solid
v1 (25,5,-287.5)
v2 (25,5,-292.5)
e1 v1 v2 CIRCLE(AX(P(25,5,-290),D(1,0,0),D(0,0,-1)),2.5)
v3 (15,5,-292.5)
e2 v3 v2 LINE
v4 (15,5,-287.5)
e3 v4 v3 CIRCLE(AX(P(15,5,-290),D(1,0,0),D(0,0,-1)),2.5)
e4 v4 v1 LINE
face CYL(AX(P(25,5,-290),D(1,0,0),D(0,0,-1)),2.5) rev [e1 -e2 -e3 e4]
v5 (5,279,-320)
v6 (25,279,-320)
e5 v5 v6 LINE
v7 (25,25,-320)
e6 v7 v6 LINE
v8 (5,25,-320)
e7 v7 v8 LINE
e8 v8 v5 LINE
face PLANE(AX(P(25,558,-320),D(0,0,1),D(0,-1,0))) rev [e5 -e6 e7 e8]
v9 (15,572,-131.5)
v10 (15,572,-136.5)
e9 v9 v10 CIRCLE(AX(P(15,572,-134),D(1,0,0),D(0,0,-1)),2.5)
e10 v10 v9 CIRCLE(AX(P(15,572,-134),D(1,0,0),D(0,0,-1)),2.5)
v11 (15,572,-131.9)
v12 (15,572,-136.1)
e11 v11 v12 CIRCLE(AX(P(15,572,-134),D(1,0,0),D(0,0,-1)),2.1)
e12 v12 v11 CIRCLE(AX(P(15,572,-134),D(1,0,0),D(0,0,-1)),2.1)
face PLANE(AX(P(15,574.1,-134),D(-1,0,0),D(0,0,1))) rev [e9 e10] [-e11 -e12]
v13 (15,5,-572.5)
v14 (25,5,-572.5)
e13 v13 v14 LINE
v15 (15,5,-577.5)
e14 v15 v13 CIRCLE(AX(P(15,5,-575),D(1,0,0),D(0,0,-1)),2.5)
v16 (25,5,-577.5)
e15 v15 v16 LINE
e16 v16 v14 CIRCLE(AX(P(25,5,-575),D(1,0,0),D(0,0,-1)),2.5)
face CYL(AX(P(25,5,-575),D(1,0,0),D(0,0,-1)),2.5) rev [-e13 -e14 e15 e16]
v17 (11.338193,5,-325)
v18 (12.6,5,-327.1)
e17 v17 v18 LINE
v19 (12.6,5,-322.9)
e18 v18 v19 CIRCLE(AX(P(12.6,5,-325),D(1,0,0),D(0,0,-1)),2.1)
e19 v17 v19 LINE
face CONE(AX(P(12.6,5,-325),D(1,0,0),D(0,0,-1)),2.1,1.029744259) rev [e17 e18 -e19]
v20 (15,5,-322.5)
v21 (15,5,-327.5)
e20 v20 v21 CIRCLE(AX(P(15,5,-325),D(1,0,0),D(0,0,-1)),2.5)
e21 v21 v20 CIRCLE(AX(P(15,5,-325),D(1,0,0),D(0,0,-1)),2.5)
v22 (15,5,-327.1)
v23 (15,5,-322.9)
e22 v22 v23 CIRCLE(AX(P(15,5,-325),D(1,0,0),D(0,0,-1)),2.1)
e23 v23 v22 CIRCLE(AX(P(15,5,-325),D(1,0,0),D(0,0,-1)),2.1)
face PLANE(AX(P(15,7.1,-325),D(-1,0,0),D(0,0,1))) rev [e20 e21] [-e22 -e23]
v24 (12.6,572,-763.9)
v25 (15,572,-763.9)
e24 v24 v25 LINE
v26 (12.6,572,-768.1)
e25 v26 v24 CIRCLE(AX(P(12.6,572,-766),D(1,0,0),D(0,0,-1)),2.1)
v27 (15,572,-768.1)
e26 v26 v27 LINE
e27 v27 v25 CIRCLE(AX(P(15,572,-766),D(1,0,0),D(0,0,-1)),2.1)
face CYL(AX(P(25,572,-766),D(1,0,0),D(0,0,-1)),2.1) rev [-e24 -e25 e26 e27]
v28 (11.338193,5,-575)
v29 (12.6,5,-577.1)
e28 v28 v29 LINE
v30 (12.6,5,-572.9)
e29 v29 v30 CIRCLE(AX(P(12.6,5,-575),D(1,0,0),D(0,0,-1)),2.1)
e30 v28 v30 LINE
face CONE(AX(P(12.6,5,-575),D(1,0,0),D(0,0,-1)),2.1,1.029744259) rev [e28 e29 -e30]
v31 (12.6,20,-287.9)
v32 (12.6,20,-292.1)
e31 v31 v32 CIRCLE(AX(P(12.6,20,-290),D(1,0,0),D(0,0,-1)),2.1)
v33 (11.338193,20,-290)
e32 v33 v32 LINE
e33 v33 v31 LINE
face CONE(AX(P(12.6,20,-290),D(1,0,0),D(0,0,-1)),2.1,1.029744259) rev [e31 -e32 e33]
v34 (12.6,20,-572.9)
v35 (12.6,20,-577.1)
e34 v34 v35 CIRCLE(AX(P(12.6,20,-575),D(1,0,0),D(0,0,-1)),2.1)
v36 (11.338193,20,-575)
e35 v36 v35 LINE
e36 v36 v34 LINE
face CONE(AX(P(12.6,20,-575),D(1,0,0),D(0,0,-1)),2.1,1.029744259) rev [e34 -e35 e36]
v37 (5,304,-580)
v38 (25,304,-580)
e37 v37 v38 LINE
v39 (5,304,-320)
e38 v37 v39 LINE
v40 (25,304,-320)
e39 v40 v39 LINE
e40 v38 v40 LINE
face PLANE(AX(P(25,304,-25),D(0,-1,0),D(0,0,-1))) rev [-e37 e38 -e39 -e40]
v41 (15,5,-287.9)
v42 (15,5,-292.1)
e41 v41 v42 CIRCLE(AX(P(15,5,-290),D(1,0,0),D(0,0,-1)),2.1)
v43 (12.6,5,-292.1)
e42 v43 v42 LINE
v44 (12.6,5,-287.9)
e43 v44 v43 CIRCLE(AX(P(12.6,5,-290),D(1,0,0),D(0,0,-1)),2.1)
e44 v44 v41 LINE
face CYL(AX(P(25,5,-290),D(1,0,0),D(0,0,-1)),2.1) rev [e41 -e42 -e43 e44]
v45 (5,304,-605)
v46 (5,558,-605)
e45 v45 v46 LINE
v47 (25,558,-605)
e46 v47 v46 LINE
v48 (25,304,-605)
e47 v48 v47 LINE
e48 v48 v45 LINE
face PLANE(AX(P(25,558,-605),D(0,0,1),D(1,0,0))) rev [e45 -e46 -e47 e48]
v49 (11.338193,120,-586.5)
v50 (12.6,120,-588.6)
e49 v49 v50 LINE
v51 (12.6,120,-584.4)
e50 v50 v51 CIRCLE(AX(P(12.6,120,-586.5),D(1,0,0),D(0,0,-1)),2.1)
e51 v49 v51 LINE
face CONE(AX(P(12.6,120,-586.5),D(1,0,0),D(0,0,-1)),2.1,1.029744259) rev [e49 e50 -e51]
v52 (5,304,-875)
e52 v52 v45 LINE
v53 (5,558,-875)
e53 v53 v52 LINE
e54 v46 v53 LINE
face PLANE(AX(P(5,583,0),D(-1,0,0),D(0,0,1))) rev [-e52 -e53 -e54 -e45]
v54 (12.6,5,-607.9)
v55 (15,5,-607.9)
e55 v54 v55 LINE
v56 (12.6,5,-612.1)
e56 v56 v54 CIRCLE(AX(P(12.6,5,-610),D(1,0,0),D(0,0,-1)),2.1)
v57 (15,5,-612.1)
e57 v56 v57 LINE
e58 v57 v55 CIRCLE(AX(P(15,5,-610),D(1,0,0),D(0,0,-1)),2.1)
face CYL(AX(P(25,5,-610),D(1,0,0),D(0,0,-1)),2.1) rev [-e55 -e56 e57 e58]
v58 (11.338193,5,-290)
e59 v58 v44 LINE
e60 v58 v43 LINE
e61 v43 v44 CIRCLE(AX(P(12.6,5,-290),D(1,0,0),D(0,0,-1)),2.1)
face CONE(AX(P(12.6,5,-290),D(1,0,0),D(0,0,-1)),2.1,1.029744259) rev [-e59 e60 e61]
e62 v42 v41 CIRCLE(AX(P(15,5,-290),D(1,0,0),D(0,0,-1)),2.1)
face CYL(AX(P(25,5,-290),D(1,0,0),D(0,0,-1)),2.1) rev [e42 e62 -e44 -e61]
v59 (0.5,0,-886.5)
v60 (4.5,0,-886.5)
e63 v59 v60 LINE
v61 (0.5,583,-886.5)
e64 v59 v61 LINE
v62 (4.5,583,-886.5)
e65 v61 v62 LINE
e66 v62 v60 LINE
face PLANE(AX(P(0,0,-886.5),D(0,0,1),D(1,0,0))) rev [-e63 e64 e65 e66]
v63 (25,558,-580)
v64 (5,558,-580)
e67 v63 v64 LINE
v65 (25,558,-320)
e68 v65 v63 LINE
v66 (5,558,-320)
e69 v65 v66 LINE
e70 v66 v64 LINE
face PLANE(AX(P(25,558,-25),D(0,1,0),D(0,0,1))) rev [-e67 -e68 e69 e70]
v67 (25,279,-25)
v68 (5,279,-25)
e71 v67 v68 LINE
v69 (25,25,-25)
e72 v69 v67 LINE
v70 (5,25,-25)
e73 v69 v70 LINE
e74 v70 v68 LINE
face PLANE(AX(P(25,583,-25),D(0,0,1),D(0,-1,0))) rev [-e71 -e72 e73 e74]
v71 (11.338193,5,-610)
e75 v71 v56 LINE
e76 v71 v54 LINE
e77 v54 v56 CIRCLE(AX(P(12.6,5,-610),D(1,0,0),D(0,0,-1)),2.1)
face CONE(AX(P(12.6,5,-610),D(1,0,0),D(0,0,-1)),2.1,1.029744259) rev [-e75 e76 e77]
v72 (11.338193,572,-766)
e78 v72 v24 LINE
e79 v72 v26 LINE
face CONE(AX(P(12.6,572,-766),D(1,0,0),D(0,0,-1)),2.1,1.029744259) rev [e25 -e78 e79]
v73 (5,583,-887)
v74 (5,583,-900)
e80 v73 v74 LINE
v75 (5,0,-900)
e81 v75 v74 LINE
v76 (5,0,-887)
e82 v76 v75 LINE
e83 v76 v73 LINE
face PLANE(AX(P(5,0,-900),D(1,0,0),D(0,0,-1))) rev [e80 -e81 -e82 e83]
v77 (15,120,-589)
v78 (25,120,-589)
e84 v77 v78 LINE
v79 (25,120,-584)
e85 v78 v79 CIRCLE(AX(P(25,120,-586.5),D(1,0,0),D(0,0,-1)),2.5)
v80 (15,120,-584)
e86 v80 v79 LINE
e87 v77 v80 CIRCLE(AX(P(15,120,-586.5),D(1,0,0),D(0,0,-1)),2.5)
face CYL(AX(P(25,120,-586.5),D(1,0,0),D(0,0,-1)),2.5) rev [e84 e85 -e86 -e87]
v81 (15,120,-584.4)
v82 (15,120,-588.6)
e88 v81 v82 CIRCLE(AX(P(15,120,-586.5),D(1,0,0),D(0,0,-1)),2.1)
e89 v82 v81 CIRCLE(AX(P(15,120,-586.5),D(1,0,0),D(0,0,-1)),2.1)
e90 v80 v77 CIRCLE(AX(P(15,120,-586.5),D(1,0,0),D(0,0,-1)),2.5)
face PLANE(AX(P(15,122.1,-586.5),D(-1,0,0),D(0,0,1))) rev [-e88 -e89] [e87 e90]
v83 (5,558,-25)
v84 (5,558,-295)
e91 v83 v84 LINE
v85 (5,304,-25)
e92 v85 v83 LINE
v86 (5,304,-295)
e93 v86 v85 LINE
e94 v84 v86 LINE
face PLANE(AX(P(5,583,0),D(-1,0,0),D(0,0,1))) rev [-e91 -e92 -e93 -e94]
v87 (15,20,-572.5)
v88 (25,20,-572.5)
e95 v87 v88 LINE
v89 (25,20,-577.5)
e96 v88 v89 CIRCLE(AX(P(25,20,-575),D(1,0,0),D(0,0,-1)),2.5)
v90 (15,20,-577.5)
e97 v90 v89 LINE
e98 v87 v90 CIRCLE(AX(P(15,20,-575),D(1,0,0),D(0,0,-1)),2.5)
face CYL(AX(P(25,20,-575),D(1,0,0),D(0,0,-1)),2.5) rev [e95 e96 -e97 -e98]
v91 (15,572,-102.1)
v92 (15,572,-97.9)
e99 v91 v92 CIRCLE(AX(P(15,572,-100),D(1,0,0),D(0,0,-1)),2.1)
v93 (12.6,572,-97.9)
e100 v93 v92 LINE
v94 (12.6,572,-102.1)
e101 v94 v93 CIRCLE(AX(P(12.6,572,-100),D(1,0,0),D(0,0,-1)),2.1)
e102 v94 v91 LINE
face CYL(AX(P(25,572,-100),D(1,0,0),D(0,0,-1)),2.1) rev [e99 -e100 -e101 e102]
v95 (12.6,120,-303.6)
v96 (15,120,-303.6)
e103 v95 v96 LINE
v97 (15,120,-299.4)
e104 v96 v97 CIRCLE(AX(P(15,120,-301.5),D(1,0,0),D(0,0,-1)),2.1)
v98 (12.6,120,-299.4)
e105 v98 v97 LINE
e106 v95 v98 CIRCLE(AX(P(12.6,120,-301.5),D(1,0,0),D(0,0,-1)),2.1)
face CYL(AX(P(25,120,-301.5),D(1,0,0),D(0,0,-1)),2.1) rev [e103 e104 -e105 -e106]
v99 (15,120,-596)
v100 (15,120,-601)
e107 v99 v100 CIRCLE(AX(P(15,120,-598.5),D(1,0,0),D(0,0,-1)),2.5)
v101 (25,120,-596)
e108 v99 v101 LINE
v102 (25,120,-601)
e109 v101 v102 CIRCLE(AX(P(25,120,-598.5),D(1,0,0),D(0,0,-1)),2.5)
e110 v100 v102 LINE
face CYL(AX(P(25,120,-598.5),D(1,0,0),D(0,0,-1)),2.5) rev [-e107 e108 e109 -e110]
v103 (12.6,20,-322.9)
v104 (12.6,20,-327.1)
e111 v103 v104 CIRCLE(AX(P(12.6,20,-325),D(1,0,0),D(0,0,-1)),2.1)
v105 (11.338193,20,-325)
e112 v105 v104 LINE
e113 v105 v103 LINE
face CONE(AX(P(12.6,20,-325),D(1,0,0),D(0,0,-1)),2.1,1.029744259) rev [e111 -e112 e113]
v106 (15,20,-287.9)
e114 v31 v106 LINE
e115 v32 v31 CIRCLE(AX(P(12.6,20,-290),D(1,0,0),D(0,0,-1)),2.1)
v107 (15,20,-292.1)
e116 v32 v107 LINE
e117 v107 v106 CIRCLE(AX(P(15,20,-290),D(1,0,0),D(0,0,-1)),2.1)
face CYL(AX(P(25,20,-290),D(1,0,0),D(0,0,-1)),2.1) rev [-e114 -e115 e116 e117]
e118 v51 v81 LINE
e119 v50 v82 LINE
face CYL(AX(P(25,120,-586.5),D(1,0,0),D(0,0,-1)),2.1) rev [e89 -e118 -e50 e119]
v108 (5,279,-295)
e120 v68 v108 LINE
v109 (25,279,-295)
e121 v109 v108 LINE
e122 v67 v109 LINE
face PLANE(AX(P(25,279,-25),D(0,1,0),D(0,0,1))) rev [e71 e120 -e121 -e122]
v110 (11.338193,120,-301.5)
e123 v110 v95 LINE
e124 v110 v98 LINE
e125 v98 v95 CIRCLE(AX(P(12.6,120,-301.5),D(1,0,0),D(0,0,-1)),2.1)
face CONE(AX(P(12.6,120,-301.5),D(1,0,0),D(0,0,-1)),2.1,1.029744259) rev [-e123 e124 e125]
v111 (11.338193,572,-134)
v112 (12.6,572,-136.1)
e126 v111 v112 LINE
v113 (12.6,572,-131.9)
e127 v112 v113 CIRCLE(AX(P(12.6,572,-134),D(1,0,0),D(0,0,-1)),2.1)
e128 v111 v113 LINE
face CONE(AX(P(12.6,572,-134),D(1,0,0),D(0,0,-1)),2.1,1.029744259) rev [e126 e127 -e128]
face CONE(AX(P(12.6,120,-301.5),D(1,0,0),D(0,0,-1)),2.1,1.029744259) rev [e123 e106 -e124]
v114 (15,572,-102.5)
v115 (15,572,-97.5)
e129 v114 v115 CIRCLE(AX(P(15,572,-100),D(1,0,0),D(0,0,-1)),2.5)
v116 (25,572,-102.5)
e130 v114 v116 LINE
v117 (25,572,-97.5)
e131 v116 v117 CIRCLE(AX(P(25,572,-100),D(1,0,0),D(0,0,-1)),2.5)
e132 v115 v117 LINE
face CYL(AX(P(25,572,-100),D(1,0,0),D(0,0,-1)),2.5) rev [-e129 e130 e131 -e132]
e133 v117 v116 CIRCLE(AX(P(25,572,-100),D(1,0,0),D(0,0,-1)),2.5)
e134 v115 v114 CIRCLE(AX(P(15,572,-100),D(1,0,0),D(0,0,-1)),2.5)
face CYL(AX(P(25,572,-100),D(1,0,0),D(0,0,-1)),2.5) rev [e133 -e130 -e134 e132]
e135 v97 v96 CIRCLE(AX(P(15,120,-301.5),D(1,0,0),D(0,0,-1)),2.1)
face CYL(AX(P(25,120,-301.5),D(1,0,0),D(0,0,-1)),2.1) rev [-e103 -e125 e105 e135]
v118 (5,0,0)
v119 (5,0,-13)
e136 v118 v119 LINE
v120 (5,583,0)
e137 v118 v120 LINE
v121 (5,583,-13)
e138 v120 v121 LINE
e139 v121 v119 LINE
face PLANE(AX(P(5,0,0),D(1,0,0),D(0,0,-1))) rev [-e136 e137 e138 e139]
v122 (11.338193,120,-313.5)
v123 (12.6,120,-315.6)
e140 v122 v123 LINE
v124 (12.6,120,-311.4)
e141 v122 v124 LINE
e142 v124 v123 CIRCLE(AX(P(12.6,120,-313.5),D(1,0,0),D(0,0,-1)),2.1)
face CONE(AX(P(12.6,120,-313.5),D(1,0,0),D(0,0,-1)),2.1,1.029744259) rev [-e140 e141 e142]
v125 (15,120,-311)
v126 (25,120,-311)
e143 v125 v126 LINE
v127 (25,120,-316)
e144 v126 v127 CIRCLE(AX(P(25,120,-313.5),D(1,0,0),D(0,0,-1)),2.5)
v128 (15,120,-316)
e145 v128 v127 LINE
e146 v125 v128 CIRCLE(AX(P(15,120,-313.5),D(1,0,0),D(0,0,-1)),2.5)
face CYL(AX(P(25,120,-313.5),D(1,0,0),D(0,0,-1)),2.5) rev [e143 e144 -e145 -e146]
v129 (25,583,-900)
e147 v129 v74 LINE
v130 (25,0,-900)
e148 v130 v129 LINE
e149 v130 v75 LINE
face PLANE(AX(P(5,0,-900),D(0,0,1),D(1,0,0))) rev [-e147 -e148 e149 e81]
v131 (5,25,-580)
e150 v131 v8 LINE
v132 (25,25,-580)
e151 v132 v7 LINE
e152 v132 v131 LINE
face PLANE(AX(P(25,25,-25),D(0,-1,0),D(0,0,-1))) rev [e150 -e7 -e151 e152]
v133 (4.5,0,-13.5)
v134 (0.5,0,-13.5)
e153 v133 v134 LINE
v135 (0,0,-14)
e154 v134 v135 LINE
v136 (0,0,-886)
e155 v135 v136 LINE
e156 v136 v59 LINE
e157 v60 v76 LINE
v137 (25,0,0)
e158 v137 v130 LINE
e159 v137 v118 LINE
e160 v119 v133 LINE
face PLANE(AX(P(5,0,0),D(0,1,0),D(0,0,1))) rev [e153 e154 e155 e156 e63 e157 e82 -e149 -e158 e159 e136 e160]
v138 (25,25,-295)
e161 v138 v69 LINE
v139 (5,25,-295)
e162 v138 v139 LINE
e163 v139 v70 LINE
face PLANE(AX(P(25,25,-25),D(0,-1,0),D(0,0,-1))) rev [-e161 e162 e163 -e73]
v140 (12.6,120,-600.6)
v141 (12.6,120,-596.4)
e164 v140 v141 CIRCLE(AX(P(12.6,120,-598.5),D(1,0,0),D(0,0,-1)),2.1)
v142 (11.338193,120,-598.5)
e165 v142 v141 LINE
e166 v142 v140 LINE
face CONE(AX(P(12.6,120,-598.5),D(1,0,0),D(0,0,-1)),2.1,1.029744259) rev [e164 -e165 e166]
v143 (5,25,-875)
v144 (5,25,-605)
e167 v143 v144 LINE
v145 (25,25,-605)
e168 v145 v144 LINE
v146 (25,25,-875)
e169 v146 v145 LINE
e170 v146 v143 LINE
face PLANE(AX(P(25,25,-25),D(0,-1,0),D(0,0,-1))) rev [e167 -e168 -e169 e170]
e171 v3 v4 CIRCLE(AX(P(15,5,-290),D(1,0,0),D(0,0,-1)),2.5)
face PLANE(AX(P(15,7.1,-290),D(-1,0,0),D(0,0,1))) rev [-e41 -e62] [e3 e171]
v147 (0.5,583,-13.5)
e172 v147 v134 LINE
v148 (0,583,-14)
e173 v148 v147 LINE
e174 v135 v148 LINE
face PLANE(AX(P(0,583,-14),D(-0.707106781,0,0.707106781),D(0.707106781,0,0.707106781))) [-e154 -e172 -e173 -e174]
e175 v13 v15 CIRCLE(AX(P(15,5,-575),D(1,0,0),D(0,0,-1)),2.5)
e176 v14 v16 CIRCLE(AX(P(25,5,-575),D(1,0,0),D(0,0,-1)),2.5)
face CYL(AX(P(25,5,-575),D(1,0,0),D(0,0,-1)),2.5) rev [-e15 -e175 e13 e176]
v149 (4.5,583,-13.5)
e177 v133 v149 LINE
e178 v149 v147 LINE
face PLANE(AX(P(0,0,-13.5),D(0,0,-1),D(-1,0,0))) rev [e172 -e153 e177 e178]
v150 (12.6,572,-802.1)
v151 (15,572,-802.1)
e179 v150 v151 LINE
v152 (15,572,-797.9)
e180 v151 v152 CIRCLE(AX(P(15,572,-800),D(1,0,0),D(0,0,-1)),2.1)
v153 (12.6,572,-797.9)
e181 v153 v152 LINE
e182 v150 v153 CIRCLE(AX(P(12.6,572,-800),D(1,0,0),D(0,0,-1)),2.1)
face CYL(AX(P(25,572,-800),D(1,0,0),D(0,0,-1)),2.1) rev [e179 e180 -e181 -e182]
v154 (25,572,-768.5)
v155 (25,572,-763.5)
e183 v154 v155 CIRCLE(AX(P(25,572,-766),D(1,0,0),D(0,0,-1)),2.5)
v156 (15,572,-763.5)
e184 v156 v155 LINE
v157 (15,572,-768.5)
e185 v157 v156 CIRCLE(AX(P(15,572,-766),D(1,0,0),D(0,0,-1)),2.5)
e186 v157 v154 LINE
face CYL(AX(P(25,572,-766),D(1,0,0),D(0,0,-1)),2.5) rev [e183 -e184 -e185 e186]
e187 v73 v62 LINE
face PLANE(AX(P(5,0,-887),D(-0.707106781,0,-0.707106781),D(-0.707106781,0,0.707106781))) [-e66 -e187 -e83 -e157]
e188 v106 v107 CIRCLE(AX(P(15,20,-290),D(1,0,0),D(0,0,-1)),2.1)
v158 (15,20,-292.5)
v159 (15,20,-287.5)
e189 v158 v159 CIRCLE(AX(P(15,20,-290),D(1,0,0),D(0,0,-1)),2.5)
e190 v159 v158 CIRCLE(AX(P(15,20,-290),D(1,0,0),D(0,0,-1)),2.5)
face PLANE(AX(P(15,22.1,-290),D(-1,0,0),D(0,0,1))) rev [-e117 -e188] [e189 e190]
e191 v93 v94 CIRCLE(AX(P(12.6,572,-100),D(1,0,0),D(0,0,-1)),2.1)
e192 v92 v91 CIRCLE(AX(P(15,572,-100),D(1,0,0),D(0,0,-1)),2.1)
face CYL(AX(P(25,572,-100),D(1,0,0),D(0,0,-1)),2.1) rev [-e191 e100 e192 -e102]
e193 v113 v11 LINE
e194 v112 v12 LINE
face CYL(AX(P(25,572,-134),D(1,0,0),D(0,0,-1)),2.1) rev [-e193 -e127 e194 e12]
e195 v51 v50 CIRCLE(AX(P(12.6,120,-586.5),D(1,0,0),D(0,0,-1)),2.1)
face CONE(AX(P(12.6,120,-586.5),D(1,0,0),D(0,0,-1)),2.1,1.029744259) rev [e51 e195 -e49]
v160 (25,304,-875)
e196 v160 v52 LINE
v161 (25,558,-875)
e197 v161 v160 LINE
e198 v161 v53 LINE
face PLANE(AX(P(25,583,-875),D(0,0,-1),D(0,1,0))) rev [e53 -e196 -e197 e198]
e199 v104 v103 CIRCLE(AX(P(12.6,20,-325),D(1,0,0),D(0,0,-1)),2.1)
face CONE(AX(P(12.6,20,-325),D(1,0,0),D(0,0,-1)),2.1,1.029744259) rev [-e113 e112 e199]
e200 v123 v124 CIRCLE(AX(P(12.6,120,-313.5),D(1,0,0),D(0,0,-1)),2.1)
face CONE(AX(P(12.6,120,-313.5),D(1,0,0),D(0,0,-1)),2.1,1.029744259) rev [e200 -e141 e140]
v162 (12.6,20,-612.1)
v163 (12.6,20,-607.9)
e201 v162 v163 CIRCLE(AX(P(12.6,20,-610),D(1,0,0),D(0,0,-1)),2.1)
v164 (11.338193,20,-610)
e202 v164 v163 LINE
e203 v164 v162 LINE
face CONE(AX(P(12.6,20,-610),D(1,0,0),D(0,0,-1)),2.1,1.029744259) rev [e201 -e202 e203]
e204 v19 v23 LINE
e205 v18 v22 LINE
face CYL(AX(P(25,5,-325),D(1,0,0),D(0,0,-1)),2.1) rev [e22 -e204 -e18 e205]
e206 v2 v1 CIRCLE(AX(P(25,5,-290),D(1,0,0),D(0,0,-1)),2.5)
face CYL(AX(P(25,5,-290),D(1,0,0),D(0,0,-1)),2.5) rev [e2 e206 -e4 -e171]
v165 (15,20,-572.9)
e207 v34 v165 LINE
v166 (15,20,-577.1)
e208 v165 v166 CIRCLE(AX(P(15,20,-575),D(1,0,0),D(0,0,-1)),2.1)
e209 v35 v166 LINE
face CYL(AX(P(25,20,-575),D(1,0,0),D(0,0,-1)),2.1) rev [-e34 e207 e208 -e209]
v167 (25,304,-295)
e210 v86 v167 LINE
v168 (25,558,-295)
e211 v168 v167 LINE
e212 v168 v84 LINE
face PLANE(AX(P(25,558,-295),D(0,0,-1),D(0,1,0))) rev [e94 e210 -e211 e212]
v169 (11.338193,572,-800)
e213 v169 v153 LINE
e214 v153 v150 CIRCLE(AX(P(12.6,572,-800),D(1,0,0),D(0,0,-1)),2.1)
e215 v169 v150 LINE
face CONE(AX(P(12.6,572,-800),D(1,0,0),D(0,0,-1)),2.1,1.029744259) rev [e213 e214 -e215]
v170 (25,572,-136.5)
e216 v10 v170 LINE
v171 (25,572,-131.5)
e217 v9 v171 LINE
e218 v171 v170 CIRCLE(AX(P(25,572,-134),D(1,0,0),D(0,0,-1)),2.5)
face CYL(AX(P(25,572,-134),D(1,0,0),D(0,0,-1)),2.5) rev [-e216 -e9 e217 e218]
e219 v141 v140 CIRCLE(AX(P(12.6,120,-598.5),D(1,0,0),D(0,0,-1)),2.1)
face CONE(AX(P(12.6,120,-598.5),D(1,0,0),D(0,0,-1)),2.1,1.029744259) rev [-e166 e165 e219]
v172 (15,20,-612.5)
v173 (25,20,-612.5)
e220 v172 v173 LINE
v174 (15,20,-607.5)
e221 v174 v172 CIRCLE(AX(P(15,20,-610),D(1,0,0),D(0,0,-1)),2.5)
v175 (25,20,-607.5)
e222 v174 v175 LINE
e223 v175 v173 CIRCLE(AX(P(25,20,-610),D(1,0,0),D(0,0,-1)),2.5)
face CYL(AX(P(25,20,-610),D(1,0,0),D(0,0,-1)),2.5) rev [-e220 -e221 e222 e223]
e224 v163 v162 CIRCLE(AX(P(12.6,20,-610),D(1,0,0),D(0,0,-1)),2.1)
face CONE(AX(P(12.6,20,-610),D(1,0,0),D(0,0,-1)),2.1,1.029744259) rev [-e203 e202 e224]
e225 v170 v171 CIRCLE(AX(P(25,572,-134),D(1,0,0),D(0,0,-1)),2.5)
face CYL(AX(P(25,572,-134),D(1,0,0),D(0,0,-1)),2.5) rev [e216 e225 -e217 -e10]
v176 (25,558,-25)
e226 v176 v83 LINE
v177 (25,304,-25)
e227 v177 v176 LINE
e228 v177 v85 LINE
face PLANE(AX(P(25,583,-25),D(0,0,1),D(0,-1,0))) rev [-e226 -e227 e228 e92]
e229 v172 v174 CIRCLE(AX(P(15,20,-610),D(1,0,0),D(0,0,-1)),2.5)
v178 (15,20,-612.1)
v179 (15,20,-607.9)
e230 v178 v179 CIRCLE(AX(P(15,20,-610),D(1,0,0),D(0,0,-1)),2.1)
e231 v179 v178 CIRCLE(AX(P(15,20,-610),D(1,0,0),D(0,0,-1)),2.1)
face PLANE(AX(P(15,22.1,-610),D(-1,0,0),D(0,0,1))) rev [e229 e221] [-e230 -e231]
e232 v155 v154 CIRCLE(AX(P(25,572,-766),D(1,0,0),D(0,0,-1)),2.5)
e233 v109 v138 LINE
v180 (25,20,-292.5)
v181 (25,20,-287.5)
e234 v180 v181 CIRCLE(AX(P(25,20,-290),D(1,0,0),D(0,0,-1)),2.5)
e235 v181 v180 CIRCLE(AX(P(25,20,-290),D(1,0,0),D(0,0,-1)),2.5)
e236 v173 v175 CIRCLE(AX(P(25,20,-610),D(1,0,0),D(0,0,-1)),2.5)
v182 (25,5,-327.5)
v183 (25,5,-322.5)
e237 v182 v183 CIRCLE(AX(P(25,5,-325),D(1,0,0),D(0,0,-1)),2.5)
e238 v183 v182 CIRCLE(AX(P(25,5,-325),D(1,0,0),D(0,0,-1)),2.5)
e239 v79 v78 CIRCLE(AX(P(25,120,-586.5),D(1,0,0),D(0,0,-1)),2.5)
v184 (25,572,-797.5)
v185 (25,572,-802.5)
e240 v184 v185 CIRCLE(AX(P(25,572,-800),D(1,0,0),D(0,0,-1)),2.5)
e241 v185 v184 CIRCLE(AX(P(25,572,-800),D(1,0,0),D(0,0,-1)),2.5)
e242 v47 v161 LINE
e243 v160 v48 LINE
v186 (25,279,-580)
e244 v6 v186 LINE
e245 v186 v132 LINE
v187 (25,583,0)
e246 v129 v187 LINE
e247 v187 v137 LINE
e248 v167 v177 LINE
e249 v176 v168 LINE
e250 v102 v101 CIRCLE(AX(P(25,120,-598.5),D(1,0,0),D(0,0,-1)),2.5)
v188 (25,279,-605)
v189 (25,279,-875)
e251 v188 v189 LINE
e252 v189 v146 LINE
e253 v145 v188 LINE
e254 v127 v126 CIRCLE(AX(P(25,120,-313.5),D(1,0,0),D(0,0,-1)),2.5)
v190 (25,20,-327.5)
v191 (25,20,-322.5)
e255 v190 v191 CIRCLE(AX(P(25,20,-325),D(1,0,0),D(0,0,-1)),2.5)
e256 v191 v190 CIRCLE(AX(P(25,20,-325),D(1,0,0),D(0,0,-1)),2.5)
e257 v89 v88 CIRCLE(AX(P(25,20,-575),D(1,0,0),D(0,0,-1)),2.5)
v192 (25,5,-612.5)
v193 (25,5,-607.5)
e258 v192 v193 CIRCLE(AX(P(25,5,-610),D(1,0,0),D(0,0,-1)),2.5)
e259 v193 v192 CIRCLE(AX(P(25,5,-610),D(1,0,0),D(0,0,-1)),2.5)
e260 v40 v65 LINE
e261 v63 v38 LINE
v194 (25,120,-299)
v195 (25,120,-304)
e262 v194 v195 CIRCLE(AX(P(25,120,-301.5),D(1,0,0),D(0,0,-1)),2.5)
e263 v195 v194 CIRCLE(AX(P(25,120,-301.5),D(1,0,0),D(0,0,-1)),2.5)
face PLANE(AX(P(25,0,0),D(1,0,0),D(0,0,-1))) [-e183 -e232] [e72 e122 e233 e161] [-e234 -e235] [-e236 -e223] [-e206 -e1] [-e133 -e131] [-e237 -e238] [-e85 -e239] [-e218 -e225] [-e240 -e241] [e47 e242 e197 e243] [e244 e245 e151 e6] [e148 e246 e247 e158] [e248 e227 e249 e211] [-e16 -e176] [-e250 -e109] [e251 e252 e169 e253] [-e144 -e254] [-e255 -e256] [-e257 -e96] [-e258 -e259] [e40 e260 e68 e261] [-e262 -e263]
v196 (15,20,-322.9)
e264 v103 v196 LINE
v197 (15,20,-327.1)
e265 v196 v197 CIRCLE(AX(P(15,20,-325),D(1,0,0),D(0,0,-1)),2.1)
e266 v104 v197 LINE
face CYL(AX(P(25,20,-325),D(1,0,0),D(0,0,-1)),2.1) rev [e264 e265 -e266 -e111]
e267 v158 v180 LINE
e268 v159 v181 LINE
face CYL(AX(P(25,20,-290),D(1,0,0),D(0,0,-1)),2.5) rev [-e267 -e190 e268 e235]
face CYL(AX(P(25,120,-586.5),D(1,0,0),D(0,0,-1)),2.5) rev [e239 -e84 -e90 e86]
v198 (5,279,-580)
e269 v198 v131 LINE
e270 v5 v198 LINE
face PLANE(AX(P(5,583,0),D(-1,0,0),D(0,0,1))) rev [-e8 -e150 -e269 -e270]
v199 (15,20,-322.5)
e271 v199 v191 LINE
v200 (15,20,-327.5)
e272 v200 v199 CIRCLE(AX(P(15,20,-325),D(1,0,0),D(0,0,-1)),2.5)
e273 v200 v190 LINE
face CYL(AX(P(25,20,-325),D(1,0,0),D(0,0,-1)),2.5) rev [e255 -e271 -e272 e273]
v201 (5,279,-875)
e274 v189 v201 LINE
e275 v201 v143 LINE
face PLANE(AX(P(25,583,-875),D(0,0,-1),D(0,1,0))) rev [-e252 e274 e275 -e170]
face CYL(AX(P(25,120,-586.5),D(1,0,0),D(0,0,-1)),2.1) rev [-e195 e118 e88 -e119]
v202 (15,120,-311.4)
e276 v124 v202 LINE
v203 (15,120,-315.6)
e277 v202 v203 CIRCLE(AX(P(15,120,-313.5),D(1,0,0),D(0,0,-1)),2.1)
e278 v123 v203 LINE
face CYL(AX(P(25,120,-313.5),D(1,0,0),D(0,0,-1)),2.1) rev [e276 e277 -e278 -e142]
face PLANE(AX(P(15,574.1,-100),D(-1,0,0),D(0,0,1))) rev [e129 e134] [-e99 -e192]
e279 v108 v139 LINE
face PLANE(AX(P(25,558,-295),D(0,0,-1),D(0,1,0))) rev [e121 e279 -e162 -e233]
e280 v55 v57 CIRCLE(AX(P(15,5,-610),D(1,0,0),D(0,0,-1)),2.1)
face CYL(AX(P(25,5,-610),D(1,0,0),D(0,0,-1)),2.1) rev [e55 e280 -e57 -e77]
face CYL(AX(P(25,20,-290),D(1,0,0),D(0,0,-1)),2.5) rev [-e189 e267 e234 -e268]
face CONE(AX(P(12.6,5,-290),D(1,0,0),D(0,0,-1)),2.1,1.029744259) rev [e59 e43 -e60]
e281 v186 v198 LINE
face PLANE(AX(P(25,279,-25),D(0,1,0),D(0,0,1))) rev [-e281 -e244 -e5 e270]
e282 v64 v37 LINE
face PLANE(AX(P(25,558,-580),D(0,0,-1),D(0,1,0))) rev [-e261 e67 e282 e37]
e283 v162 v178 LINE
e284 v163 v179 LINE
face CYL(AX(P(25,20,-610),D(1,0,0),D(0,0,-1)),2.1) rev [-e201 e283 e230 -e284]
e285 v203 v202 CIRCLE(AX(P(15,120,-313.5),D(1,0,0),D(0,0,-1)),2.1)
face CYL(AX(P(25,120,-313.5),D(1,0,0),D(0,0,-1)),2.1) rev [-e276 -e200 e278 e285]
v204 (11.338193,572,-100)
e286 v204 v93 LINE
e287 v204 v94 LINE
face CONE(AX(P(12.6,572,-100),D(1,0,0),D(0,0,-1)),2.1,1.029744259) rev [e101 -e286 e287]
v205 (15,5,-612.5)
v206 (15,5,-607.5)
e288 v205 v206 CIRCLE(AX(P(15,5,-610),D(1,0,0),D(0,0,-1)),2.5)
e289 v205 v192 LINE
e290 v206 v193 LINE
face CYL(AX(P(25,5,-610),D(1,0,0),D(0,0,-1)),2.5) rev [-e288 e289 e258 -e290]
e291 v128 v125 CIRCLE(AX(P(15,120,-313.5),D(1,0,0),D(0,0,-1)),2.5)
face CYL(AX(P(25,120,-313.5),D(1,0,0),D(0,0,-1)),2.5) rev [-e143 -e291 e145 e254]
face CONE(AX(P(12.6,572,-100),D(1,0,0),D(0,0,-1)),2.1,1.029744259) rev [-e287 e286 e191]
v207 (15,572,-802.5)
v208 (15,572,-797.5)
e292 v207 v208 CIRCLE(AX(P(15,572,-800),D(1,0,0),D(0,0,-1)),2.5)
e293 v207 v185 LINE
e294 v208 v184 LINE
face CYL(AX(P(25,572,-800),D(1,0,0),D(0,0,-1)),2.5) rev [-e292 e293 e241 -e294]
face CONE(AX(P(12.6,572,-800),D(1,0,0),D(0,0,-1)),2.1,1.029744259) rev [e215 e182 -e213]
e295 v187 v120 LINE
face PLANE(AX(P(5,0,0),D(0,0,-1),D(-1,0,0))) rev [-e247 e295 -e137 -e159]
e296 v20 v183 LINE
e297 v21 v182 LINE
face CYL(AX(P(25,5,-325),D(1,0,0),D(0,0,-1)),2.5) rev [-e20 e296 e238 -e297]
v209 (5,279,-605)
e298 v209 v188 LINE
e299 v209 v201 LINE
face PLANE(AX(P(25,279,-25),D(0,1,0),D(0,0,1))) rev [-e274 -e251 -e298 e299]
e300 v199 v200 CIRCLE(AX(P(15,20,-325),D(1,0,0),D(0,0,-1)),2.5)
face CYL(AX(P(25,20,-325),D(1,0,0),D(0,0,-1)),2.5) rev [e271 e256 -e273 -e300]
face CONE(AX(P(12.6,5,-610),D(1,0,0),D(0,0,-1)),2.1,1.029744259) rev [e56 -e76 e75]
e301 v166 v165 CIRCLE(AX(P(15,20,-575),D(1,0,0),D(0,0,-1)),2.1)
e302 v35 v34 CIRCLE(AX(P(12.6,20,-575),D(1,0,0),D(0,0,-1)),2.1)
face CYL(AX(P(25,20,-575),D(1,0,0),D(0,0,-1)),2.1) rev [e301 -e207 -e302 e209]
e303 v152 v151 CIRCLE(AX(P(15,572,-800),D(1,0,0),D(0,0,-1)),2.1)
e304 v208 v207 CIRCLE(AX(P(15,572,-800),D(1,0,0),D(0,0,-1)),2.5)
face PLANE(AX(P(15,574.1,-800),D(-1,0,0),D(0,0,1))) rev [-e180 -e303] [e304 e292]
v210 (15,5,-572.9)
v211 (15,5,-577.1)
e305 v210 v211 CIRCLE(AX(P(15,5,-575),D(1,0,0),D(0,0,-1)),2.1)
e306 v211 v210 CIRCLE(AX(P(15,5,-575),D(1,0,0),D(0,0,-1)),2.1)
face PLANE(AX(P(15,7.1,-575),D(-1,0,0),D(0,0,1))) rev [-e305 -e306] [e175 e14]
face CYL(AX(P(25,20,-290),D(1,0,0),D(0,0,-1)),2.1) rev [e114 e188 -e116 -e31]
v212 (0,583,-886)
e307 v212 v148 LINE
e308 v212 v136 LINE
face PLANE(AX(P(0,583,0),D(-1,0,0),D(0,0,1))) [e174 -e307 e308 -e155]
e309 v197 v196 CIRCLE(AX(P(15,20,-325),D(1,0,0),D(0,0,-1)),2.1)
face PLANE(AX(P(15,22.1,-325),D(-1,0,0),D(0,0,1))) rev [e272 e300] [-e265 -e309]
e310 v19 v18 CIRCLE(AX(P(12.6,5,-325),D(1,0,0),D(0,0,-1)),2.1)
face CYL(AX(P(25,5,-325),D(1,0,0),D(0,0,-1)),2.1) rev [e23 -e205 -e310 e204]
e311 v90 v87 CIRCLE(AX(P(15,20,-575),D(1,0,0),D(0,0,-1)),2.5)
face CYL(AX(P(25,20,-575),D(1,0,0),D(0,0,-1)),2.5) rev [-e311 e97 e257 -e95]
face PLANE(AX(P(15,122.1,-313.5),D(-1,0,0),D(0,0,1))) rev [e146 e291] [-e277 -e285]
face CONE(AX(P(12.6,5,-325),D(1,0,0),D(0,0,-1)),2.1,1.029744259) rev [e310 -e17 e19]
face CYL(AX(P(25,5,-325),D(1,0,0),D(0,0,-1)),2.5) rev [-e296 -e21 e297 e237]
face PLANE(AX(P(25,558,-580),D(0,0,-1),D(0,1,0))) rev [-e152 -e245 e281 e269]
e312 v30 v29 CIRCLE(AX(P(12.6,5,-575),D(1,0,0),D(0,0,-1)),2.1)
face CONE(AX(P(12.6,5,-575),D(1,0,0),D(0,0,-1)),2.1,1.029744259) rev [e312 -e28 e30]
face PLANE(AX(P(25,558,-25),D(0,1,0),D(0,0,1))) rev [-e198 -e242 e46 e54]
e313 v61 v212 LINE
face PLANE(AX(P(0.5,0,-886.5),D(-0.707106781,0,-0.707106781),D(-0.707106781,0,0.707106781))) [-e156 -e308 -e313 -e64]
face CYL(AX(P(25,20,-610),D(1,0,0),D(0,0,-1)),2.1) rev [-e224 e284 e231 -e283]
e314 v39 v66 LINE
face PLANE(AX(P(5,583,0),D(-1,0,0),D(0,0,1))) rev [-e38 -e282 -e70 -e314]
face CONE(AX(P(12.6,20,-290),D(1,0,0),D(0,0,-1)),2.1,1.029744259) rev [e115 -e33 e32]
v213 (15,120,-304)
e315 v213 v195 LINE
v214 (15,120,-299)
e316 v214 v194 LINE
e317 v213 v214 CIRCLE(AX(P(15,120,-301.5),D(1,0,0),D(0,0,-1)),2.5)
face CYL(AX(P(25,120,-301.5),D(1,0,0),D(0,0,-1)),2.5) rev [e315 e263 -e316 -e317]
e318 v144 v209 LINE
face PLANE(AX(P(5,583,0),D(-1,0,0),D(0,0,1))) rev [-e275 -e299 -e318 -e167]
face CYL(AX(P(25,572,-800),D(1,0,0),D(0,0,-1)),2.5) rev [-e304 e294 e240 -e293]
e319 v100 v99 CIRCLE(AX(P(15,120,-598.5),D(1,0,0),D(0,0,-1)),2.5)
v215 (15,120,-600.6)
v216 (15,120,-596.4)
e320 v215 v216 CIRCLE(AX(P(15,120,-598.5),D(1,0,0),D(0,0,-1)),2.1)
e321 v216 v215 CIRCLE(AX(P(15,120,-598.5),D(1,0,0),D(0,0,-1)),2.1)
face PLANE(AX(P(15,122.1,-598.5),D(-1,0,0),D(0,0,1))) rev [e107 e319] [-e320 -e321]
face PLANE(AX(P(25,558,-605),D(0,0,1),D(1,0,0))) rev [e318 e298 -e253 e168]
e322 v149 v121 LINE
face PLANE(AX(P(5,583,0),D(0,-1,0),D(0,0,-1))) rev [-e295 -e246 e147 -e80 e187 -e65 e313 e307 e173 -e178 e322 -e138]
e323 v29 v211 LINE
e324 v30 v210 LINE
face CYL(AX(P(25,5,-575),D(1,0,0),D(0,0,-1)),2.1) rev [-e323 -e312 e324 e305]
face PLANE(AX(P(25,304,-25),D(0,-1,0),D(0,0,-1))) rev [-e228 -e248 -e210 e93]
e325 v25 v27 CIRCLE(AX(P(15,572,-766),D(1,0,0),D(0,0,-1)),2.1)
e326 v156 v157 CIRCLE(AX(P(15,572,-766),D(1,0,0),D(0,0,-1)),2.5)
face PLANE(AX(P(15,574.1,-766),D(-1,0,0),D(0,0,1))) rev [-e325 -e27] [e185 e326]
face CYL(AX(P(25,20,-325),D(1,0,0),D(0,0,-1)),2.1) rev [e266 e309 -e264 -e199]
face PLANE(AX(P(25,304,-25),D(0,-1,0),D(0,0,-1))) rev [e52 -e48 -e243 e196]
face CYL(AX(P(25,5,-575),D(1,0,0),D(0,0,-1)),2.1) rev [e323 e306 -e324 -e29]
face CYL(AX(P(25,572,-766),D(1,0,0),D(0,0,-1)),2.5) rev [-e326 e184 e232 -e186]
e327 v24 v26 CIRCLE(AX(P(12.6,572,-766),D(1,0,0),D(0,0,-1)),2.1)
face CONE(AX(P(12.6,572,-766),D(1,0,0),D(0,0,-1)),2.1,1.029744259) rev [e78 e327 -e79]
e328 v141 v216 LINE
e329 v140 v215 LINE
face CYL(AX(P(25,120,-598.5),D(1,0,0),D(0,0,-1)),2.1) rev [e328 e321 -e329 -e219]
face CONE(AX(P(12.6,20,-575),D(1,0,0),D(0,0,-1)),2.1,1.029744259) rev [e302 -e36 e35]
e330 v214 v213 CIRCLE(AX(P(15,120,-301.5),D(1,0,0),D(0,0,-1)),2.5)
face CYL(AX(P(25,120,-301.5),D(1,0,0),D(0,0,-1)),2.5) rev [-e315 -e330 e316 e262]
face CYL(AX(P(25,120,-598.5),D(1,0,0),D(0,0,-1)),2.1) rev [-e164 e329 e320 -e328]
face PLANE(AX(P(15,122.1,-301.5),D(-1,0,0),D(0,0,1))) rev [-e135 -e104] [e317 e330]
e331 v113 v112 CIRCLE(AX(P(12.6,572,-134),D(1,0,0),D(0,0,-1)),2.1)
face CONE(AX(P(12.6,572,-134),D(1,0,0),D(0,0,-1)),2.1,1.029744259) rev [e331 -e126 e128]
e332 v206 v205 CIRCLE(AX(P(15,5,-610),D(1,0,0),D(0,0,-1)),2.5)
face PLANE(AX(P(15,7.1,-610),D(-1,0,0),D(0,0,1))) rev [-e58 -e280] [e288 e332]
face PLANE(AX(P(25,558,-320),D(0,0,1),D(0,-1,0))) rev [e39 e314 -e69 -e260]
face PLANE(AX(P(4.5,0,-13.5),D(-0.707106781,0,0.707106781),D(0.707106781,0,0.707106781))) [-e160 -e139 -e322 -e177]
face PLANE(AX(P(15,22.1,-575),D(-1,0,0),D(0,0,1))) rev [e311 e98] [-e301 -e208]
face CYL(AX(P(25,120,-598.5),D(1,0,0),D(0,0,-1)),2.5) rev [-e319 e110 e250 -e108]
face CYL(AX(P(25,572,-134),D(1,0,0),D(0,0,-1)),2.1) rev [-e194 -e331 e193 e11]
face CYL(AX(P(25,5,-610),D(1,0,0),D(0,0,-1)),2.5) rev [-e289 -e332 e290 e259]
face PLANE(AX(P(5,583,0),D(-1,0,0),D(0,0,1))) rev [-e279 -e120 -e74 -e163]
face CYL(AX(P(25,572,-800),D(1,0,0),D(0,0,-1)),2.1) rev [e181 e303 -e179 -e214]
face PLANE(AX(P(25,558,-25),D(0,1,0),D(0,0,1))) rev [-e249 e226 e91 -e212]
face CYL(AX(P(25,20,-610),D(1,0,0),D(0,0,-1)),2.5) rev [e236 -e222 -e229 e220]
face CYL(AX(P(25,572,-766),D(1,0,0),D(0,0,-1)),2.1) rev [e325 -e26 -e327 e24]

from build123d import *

# Parameters (mm, degrees)
SKETCH_1_W                  = 900
SKETCH_1_H                  = 583
EXTRUDE_1_DEPTH             = 5
SKETCH_2_W                  = 25
SKETCH_2_H                  = 583
EXTRUDE_2_DEPTH             = 20
SKETCH_3_W                  = 850
SKETCH_3_H                  = 25
EXTRUDE_3_DEPTH             = 20
SKETCH_4_W                  = 850
SKETCH_4_H                  = 25
EXTRUDE_4_DEPTH             = 20
SKETCH_5_W                  = 25
SKETCH_5_H                  = 533
EXTRUDE_5_DEPTH             = 20
SKETCH_6_W                  = 5
SKETCH_6_H                  = 13.5
CUT_EXTRUDE_1_DEPTH         = 1073.620156439
CHAMFER_1_SIZE              = 0.5
SKETCH_7_W                  = 5
SKETCH_7_H                  = 13.5
CUT_EXTRUDE_2_DEPTH         = 1073.620156439
CHAMFER_2_SIZE              = 0.5
PATTERN_LINEAR_1_COUNT      = 2
PATTERN_LINEAR_1_PITCH      = 35
PATTERN_LINEAR_1_COUNT_DIR2 = 2
PATTERN_LINEAR_1_PITCH_DIR2 = 15
HOLE_WIZARD_M5_2_AT_2_COUNT = 2
HOLE_WIZARD_M5_2_AT_2_PITCH = 12
PATTERN_LINEAR_2_COUNT      = 2
PATTERN_LINEAR_2_PITCH      = 285
HOLE_WIZARD_M5_3_AT_2_COUNT = 2
HOLE_WIZARD_M5_3_AT_2_PITCH = 34
PATTERN_LINEAR_3_COUNT      = 2
PATTERN_LINEAR_3_PITCH      = 666


with BuildPart() as part:
    # 草图1 → 拉伸1 (new body)
    with BuildSketch(Plane(origin=(0, 0, 0), x_dir=(0, 0, -1), z_dir=(1, 0, 0))):
        with Locations((450, 291.5)):
            Rectangle(SKETCH_1_W, SKETCH_1_H)
    extrude(amount=EXTRUDE_1_DEPTH)

    # 草图2 → 拉伸2 (add)
    with BuildSketch(Plane(origin=(5, 0, 0), x_dir=(0, 0, -1), z_dir=(1, 0, 0))):
        with Locations((12.5, 291.5)):
            Rectangle(SKETCH_2_W, SKETCH_2_H)
        with Locations((887.5, 291.5)):
            Rectangle(SKETCH_2_W, SKETCH_2_H)
    extrude(amount=EXTRUDE_2_DEPTH)

    # 草图3 → 拉伸3 (add)
    with BuildSketch(Plane(origin=(5, 0, 0), x_dir=(0, 0, -1), z_dir=(1, 0, 0))):
        with Locations((450, 570.5)):
            Rectangle(SKETCH_3_W, SKETCH_3_H)
        with Locations((450, 12.5)):
            Rectangle(SKETCH_3_W, SKETCH_3_H)
    extrude(amount=EXTRUDE_3_DEPTH)

    # 草图4 → 拉伸4 (add)
    with BuildSketch(Plane(origin=(5, 0, 0), x_dir=(0, 0, -1), z_dir=(1, 0, 0))):
        with Locations((450, 291.5)):
            Rectangle(SKETCH_4_W, SKETCH_4_H)
    extrude(amount=EXTRUDE_4_DEPTH)

    # 草图5 → 拉伸5 (add)
    with BuildSketch(Plane(origin=(5, 0, 0), x_dir=(0, 0, -1), z_dir=(1, 0, 0))):
        with Locations((307.5, 291.5)):
            Rectangle(SKETCH_5_W, SKETCH_5_H)
        with Locations((592.5, 291.5)):
            Rectangle(SKETCH_5_W, SKETCH_5_H)
    extrude(amount=EXTRUDE_5_DEPTH)

    # 草图6 → 切除-拉伸1 (cut, through all)
    with BuildSketch(Plane(origin=(0, 583, 0), x_dir=(-1, 0, 0), z_dir=(0, 1, 0))):
        with Locations((-2.5, -6.75)):
            Rectangle(SKETCH_6_W, SKETCH_6_H)
    extrude(amount=-CUT_EXTRUDE_1_DEPTH, mode=Mode.SUBTRACT)

    # 倒角1
    chamfer_1_edges = [part.edges().sort_by_distance(p)[0] for p in [
        (0, 291.5, -13.5),
        (5, 291.5, -13.5),
    ]]
    chamfer(chamfer_1_edges, length=CHAMFER_1_SIZE)

    # 草图7 → 切除-拉伸2 (cut, through all)
    with BuildSketch(Plane(origin=(0, 583, 0), x_dir=(-1, 0, 0), z_dir=(0, 1, 0))):
        with Locations((-2.5, -893.25)):
            Rectangle(SKETCH_7_W, SKETCH_7_H)
    extrude(amount=-CUT_EXTRUDE_2_DEPTH, mode=Mode.SUBTRACT)

    # 倒角2
    chamfer_2_edges = [part.edges().sort_by_distance(p)[0] for p in [
        (0, 291.5, -886.5),
        (5, 291.5, -886.5),
    ]]
    chamfer(chamfer_2_edges, length=CHAMFER_2_SIZE)

    # 草图8 → M5 螺纹孔1 (revolve, cut)
    with BuildSketch(Plane(origin=(25, 5, -290), x_dir=(0, 0, -1), z_dir=(0, 1, 0))):
        Polygon((0, 0), (0, 13.6618073), (2.1, 12.4), (2.1, 10), (2.5, 10), (2.5, 0), align=None)
    hole_wizard_m5_1 = revolve(axis=Axis((31.35, 5, -290), (-1, 0, 0)), mode=Mode.SUBTRACT)

    # 阵列(线性)1: Hole Wizard M5 _1 2 × 2
    with Locations(*[(0, j * PATTERN_LINEAR_1_PITCH_DIR2, -i * PATTERN_LINEAR_1_PITCH) for i in range(PATTERN_LINEAR_1_COUNT) for j in range(PATTERN_LINEAR_1_COUNT_DIR2) if (i, j) != (0, 0)]):
        add(hole_wizard_m5_1, mode=Mode.SUBTRACT)

    # 草图9 → M5 螺纹孔2 (revolve, cut)
    with BuildSketch(Plane(origin=(25, 120, -301.5), x_dir=(0, 0, -1), z_dir=(0, 1, 0))):
        Polygon((0, 0), (0, 13.6618073), (2.1, 12.4), (2.1, 10), (2.5, 10), (2.5, 0), align=None)
    hole_wizard_m5_2 = revolve(axis=Axis((31.35, 120, -301.5), (-1, 0, 0)), mode=Mode.SUBTRACT)

    # M5 螺纹孔2 at 2: M5 螺纹孔2 ×2
    with Locations(*[(0, 0, -i * HOLE_WIZARD_M5_2_AT_2_PITCH) for i in range(1, HOLE_WIZARD_M5_2_AT_2_COUNT)]):
        add(hole_wizard_m5_2, mode=Mode.SUBTRACT)

    # 阵列(线性)2: M5 螺纹孔1, M5 螺纹孔2 ×2
    with Locations(*[(0, 0, -i * PATTERN_LINEAR_2_PITCH) for i in range(1, PATTERN_LINEAR_2_COUNT)]):
        add(hole_wizard_m5_1, mode=Mode.SUBTRACT)
        add(hole_wizard_m5_2, mode=Mode.SUBTRACT)

    # 阵列(线性)2 copy 1 sketch → 阵列(线性)2 copy 1 (revolve, cut)
    with BuildSketch(Plane(origin=(25, 20, -575), x_dir=(0, 0, -1), z_dir=(0, 1, 0))):
        Polygon((0, 0), (0, 13.6618073), (2.1, 12.4), (2.1, 10), (2.5, 10), (2.5, 0), align=None)
    revolve(axis=Axis((31.35, 20, -575), (-1, 0, 0)), mode=Mode.SUBTRACT)

    # 阵列(线性)2 copy 2 sketch → 阵列(线性)2 copy 2 (revolve, cut)
    with BuildSketch(Plane(origin=(25, 5, -610), x_dir=(0, 0, -1), z_dir=(0, 1, 0))):
        Polygon((0, 0), (0, 13.6618073), (2.1, 12.4), (2.1, 10), (2.5, 10), (2.5, 0), align=None)
    revolve(axis=Axis((31.35, 5, -610), (-1, 0, 0)), mode=Mode.SUBTRACT)

    # 阵列(线性)2 copy 3 sketch → 阵列(线性)2 copy 3 (revolve, cut)
    with BuildSketch(Plane(origin=(25, 20, -610), x_dir=(0, 0, -1), z_dir=(0, 1, 0))):
        Polygon((0, 0), (0, 13.6618073), (2.1, 12.4), (2.1, 10), (2.5, 10), (2.5, 0), align=None)
    revolve(axis=Axis((31.35, 20, -610), (-1, 0, 0)), mode=Mode.SUBTRACT)

    # 阵列(线性)2 copy 4 sketch → 阵列(线性)2 copy 4 (revolve, cut)
    with BuildSketch(Plane(origin=(25, 120, -598.5), x_dir=(0, 0, -1), z_dir=(0, 1, 0))):
        Polygon((0, 0), (0, 13.6618073), (2.1, 12.4), (2.1, 10), (2.5, 10), (2.5, 0), align=None)
    revolve(axis=Axis((31.35, 120, -598.5), (-1, 0, 0)), mode=Mode.SUBTRACT)

    # 草图10 → M5 螺纹孔3 (revolve, cut)
    with BuildSketch(Plane(origin=(25, 572, -100), x_dir=(0, 0, -1), z_dir=(0, 1, 0))):
        Polygon((0, 0), (0, 13.6618073), (2.1, 12.4), (2.1, 10), (2.5, 10), (2.5, 0), align=None)
    hole_wizard_m5_3 = revolve(axis=Axis((31.35, 572, -100), (-1, 0, 0)), mode=Mode.SUBTRACT)

    # M5 螺纹孔3 at 2: M5 螺纹孔3 ×2
    with Locations(*[(0, 0, -i * HOLE_WIZARD_M5_3_AT_2_PITCH) for i in range(1, HOLE_WIZARD_M5_3_AT_2_COUNT)]):
        add(hole_wizard_m5_3, mode=Mode.SUBTRACT)

    # 阵列(线性)3: M5 螺纹孔3 ×2
    with Locations(*[(0, 0, -i * PATTERN_LINEAR_3_PITCH) for i in range(1, PATTERN_LINEAR_3_COUNT)]):
        add(hole_wizard_m5_3, mode=Mode.SUBTRACT)

    # 阵列(线性)3 copy 1 sketch → 阵列(线性)3 copy 1 (revolve, cut)
    with BuildSketch(Plane(origin=(25, 572, -800), x_dir=(0, 0, -1), z_dir=(0, 1, 0))):
        Polygon((0, 0), (0, 13.6618073), (2.1, 12.4), (2.1, 10), (2.5, 10), (2.5, 0), align=None)
    revolve(axis=Axis((31.35, 572, -800), (-1, 0, 0)), mode=Mode.SUBTRACT)


solid = part.part
